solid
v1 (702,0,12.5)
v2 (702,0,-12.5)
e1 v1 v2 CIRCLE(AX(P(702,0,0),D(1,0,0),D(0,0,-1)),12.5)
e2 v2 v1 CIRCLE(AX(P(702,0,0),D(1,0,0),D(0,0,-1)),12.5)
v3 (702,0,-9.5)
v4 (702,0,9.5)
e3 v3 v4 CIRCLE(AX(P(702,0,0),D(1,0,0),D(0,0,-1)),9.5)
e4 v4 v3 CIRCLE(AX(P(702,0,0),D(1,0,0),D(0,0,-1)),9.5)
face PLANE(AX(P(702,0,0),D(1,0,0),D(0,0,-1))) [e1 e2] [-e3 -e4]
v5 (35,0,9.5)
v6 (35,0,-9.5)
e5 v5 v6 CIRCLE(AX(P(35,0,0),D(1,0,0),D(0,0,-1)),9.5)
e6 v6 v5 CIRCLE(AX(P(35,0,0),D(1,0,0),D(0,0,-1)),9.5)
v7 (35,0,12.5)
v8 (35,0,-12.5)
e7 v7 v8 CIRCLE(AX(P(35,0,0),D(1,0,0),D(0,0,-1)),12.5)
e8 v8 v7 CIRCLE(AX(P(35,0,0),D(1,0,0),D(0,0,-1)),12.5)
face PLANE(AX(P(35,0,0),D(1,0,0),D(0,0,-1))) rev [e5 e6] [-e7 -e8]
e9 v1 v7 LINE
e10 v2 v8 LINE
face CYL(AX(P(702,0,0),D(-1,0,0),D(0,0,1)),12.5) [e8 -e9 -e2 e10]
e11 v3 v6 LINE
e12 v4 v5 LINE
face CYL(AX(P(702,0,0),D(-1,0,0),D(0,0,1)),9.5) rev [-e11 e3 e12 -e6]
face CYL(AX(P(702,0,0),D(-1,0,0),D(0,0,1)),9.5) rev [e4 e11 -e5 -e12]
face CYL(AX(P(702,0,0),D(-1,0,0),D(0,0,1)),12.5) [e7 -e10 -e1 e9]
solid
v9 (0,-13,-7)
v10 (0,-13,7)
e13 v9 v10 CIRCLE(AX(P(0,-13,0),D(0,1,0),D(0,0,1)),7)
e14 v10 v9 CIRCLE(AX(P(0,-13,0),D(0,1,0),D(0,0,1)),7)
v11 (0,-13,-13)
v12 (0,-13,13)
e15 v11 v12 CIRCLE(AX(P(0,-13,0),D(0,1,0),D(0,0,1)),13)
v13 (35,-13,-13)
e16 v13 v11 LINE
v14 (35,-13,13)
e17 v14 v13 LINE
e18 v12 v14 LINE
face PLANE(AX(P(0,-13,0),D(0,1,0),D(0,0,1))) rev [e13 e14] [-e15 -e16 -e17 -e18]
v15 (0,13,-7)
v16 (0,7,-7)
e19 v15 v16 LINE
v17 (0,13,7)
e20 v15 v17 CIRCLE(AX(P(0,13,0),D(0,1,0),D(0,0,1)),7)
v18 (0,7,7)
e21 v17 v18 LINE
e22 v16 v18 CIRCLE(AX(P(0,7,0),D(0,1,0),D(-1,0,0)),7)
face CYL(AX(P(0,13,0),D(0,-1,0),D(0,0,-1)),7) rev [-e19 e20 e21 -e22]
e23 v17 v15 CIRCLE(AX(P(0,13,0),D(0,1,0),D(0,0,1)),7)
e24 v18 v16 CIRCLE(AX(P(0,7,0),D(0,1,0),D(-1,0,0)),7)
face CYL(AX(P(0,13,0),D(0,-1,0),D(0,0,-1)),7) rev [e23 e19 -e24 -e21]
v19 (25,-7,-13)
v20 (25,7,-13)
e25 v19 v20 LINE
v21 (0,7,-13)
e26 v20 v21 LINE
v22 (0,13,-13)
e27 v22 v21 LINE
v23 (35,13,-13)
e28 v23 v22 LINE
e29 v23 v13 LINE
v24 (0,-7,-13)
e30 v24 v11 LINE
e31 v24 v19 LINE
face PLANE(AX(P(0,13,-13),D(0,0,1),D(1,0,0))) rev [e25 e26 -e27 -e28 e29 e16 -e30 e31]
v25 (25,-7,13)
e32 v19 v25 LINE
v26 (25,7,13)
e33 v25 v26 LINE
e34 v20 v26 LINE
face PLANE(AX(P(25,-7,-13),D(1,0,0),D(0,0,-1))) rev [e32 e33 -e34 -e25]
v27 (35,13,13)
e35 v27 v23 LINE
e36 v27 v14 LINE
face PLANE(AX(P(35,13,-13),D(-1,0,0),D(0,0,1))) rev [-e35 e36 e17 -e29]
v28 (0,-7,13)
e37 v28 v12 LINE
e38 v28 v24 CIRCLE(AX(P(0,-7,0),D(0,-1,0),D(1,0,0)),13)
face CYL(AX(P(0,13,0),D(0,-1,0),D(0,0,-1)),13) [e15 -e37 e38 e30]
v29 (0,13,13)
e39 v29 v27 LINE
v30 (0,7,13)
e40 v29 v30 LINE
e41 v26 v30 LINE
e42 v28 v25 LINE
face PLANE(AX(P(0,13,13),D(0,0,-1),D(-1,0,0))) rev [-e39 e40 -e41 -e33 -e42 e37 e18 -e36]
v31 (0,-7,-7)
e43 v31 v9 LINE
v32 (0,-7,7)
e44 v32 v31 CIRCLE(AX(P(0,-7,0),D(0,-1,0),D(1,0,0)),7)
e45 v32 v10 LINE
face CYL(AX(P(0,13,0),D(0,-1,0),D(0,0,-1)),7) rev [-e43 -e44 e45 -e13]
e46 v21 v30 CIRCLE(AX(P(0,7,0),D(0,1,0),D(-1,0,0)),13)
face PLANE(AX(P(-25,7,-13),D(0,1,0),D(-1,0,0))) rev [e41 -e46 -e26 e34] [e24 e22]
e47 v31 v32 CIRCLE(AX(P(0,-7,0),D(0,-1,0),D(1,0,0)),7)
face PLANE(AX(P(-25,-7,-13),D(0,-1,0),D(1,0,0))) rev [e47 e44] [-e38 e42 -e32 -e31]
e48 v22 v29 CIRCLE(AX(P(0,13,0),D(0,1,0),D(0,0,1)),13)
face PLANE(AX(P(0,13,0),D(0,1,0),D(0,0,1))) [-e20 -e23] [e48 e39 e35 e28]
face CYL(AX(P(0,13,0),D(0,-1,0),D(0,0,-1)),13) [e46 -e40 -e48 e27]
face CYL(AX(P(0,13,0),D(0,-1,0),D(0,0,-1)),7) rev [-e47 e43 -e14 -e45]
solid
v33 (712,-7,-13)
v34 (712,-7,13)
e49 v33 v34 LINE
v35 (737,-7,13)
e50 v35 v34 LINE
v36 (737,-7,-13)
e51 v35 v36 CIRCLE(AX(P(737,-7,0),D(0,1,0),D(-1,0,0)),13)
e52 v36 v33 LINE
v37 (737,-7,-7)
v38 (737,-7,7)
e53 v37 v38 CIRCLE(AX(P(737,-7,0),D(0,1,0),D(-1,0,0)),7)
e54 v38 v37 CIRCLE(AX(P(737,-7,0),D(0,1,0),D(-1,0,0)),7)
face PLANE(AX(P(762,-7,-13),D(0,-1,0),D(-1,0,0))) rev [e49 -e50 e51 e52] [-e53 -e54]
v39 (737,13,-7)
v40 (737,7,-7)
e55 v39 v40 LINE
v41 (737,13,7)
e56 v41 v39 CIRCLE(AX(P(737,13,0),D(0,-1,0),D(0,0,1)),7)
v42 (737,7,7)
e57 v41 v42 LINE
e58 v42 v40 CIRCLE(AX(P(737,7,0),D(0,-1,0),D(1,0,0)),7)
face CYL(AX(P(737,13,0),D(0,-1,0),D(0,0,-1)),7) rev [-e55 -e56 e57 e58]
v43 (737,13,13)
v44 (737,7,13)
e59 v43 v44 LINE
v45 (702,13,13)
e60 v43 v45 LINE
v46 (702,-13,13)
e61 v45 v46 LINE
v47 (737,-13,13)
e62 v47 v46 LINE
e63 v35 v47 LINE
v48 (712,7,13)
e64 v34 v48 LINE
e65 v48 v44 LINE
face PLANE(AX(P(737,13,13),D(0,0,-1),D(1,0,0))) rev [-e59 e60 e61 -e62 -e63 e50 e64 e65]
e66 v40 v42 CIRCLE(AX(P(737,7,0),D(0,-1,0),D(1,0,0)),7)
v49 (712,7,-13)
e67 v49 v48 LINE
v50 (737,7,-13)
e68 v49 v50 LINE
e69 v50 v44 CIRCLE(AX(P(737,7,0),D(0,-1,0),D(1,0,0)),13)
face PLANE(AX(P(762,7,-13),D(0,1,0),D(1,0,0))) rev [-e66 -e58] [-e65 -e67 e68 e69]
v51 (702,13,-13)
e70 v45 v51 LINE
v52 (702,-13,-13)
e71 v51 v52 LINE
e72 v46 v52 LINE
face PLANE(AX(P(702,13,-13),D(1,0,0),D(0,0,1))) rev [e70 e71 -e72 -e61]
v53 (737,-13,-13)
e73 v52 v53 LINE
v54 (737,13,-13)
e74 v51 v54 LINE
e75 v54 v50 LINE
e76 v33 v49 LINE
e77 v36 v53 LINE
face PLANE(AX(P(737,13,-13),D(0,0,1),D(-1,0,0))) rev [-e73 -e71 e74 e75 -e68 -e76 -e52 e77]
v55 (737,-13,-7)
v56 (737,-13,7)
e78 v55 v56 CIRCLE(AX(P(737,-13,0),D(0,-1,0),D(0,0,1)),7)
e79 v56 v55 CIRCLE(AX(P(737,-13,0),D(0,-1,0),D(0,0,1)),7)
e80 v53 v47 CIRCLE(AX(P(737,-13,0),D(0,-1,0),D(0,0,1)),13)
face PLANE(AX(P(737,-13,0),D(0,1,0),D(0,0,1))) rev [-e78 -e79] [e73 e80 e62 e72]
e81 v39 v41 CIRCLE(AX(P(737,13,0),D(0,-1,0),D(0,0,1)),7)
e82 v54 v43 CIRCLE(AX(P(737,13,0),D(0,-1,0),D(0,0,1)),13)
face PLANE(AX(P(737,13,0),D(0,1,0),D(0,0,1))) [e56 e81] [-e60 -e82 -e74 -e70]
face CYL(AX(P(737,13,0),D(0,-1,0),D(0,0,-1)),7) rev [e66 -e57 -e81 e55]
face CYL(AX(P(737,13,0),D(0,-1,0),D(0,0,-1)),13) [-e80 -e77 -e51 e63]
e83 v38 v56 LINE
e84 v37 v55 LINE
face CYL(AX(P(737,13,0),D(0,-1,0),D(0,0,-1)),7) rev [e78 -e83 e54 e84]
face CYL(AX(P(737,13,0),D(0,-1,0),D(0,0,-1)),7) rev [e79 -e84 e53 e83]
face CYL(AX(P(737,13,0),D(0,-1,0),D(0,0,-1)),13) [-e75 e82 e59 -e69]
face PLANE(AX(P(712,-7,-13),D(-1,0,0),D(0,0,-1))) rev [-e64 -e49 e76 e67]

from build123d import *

# Parameters (mm, degrees)
SKETCH_1_R               = 7
EXTRUDE_1_DEPTH          = 13
CUT_EXTRUDE_1_DEPTH      = 40.534794802
CUT_EXTRUDE_1_DEPTH_BACK = 40.534794802
SKETCH_2_W               = 50
SKETCH_2_H               = 14
SKETCH_3_R               = 12.5
SKETCH_3_R_2             = 9.5
EXTRUDE_2_DEPTH          = 667


with BuildPart() as part:
    # 草图1 → 凸台-拉伸1 (new, symmetric)
    with BuildSketch(Plane(origin=(0, 0, 0), x_dir=(1, 0, 0), z_dir=(0, 1, 0))):
        with BuildLine():
            Line((0, 13), (35, 13))
            Line((35, 13), (35, -13))
            Line((35, -13), (0, -13))
            ThreePointArc((0, -13), (-13, 0), (0, 13))
        make_face()
        with Locations(Location((0, 0, 0), (0, 0, 90))):
            Circle(SKETCH_1_R, mode=Mode.SUBTRACT)
    extrude(amount=EXTRUDE_1_DEPTH, both=True)

    # 草图2 → 切除-拉伸1 (cut, two sides: drawn at the far end of the back side and taken through both)
    with BuildSketch(Plane.XY.offset(-CUT_EXTRUDE_1_DEPTH_BACK)):
        Rectangle(SKETCH_2_W, SKETCH_2_H)
    extrude(amount=CUT_EXTRUDE_1_DEPTH + CUT_EXTRUDE_1_DEPTH_BACK, mode=Mode.SUBTRACT)


with BuildPart() as body_2:
    # 草图3 → 凸台-拉伸2 (new body)
    with BuildSketch(Plane(origin=(35, 0, 0), x_dir=(0, 0, -1), z_dir=(1, 0, 0))):
        Circle(SKETCH_3_R)
        Circle(SKETCH_3_R_2, mode=Mode.SUBTRACT)
    extrude(amount=EXTRUDE_2_DEPTH)


with BuildPart() as body_3:
    # 镜向1: mirrored copy
    add(part.part.mirror(Plane(origin=(368.5, 0, 0), x_dir=(0, 0, 1), z_dir=(1, 0, 0))))


solid = Compound([part.part, body_2.part, body_3.part])
